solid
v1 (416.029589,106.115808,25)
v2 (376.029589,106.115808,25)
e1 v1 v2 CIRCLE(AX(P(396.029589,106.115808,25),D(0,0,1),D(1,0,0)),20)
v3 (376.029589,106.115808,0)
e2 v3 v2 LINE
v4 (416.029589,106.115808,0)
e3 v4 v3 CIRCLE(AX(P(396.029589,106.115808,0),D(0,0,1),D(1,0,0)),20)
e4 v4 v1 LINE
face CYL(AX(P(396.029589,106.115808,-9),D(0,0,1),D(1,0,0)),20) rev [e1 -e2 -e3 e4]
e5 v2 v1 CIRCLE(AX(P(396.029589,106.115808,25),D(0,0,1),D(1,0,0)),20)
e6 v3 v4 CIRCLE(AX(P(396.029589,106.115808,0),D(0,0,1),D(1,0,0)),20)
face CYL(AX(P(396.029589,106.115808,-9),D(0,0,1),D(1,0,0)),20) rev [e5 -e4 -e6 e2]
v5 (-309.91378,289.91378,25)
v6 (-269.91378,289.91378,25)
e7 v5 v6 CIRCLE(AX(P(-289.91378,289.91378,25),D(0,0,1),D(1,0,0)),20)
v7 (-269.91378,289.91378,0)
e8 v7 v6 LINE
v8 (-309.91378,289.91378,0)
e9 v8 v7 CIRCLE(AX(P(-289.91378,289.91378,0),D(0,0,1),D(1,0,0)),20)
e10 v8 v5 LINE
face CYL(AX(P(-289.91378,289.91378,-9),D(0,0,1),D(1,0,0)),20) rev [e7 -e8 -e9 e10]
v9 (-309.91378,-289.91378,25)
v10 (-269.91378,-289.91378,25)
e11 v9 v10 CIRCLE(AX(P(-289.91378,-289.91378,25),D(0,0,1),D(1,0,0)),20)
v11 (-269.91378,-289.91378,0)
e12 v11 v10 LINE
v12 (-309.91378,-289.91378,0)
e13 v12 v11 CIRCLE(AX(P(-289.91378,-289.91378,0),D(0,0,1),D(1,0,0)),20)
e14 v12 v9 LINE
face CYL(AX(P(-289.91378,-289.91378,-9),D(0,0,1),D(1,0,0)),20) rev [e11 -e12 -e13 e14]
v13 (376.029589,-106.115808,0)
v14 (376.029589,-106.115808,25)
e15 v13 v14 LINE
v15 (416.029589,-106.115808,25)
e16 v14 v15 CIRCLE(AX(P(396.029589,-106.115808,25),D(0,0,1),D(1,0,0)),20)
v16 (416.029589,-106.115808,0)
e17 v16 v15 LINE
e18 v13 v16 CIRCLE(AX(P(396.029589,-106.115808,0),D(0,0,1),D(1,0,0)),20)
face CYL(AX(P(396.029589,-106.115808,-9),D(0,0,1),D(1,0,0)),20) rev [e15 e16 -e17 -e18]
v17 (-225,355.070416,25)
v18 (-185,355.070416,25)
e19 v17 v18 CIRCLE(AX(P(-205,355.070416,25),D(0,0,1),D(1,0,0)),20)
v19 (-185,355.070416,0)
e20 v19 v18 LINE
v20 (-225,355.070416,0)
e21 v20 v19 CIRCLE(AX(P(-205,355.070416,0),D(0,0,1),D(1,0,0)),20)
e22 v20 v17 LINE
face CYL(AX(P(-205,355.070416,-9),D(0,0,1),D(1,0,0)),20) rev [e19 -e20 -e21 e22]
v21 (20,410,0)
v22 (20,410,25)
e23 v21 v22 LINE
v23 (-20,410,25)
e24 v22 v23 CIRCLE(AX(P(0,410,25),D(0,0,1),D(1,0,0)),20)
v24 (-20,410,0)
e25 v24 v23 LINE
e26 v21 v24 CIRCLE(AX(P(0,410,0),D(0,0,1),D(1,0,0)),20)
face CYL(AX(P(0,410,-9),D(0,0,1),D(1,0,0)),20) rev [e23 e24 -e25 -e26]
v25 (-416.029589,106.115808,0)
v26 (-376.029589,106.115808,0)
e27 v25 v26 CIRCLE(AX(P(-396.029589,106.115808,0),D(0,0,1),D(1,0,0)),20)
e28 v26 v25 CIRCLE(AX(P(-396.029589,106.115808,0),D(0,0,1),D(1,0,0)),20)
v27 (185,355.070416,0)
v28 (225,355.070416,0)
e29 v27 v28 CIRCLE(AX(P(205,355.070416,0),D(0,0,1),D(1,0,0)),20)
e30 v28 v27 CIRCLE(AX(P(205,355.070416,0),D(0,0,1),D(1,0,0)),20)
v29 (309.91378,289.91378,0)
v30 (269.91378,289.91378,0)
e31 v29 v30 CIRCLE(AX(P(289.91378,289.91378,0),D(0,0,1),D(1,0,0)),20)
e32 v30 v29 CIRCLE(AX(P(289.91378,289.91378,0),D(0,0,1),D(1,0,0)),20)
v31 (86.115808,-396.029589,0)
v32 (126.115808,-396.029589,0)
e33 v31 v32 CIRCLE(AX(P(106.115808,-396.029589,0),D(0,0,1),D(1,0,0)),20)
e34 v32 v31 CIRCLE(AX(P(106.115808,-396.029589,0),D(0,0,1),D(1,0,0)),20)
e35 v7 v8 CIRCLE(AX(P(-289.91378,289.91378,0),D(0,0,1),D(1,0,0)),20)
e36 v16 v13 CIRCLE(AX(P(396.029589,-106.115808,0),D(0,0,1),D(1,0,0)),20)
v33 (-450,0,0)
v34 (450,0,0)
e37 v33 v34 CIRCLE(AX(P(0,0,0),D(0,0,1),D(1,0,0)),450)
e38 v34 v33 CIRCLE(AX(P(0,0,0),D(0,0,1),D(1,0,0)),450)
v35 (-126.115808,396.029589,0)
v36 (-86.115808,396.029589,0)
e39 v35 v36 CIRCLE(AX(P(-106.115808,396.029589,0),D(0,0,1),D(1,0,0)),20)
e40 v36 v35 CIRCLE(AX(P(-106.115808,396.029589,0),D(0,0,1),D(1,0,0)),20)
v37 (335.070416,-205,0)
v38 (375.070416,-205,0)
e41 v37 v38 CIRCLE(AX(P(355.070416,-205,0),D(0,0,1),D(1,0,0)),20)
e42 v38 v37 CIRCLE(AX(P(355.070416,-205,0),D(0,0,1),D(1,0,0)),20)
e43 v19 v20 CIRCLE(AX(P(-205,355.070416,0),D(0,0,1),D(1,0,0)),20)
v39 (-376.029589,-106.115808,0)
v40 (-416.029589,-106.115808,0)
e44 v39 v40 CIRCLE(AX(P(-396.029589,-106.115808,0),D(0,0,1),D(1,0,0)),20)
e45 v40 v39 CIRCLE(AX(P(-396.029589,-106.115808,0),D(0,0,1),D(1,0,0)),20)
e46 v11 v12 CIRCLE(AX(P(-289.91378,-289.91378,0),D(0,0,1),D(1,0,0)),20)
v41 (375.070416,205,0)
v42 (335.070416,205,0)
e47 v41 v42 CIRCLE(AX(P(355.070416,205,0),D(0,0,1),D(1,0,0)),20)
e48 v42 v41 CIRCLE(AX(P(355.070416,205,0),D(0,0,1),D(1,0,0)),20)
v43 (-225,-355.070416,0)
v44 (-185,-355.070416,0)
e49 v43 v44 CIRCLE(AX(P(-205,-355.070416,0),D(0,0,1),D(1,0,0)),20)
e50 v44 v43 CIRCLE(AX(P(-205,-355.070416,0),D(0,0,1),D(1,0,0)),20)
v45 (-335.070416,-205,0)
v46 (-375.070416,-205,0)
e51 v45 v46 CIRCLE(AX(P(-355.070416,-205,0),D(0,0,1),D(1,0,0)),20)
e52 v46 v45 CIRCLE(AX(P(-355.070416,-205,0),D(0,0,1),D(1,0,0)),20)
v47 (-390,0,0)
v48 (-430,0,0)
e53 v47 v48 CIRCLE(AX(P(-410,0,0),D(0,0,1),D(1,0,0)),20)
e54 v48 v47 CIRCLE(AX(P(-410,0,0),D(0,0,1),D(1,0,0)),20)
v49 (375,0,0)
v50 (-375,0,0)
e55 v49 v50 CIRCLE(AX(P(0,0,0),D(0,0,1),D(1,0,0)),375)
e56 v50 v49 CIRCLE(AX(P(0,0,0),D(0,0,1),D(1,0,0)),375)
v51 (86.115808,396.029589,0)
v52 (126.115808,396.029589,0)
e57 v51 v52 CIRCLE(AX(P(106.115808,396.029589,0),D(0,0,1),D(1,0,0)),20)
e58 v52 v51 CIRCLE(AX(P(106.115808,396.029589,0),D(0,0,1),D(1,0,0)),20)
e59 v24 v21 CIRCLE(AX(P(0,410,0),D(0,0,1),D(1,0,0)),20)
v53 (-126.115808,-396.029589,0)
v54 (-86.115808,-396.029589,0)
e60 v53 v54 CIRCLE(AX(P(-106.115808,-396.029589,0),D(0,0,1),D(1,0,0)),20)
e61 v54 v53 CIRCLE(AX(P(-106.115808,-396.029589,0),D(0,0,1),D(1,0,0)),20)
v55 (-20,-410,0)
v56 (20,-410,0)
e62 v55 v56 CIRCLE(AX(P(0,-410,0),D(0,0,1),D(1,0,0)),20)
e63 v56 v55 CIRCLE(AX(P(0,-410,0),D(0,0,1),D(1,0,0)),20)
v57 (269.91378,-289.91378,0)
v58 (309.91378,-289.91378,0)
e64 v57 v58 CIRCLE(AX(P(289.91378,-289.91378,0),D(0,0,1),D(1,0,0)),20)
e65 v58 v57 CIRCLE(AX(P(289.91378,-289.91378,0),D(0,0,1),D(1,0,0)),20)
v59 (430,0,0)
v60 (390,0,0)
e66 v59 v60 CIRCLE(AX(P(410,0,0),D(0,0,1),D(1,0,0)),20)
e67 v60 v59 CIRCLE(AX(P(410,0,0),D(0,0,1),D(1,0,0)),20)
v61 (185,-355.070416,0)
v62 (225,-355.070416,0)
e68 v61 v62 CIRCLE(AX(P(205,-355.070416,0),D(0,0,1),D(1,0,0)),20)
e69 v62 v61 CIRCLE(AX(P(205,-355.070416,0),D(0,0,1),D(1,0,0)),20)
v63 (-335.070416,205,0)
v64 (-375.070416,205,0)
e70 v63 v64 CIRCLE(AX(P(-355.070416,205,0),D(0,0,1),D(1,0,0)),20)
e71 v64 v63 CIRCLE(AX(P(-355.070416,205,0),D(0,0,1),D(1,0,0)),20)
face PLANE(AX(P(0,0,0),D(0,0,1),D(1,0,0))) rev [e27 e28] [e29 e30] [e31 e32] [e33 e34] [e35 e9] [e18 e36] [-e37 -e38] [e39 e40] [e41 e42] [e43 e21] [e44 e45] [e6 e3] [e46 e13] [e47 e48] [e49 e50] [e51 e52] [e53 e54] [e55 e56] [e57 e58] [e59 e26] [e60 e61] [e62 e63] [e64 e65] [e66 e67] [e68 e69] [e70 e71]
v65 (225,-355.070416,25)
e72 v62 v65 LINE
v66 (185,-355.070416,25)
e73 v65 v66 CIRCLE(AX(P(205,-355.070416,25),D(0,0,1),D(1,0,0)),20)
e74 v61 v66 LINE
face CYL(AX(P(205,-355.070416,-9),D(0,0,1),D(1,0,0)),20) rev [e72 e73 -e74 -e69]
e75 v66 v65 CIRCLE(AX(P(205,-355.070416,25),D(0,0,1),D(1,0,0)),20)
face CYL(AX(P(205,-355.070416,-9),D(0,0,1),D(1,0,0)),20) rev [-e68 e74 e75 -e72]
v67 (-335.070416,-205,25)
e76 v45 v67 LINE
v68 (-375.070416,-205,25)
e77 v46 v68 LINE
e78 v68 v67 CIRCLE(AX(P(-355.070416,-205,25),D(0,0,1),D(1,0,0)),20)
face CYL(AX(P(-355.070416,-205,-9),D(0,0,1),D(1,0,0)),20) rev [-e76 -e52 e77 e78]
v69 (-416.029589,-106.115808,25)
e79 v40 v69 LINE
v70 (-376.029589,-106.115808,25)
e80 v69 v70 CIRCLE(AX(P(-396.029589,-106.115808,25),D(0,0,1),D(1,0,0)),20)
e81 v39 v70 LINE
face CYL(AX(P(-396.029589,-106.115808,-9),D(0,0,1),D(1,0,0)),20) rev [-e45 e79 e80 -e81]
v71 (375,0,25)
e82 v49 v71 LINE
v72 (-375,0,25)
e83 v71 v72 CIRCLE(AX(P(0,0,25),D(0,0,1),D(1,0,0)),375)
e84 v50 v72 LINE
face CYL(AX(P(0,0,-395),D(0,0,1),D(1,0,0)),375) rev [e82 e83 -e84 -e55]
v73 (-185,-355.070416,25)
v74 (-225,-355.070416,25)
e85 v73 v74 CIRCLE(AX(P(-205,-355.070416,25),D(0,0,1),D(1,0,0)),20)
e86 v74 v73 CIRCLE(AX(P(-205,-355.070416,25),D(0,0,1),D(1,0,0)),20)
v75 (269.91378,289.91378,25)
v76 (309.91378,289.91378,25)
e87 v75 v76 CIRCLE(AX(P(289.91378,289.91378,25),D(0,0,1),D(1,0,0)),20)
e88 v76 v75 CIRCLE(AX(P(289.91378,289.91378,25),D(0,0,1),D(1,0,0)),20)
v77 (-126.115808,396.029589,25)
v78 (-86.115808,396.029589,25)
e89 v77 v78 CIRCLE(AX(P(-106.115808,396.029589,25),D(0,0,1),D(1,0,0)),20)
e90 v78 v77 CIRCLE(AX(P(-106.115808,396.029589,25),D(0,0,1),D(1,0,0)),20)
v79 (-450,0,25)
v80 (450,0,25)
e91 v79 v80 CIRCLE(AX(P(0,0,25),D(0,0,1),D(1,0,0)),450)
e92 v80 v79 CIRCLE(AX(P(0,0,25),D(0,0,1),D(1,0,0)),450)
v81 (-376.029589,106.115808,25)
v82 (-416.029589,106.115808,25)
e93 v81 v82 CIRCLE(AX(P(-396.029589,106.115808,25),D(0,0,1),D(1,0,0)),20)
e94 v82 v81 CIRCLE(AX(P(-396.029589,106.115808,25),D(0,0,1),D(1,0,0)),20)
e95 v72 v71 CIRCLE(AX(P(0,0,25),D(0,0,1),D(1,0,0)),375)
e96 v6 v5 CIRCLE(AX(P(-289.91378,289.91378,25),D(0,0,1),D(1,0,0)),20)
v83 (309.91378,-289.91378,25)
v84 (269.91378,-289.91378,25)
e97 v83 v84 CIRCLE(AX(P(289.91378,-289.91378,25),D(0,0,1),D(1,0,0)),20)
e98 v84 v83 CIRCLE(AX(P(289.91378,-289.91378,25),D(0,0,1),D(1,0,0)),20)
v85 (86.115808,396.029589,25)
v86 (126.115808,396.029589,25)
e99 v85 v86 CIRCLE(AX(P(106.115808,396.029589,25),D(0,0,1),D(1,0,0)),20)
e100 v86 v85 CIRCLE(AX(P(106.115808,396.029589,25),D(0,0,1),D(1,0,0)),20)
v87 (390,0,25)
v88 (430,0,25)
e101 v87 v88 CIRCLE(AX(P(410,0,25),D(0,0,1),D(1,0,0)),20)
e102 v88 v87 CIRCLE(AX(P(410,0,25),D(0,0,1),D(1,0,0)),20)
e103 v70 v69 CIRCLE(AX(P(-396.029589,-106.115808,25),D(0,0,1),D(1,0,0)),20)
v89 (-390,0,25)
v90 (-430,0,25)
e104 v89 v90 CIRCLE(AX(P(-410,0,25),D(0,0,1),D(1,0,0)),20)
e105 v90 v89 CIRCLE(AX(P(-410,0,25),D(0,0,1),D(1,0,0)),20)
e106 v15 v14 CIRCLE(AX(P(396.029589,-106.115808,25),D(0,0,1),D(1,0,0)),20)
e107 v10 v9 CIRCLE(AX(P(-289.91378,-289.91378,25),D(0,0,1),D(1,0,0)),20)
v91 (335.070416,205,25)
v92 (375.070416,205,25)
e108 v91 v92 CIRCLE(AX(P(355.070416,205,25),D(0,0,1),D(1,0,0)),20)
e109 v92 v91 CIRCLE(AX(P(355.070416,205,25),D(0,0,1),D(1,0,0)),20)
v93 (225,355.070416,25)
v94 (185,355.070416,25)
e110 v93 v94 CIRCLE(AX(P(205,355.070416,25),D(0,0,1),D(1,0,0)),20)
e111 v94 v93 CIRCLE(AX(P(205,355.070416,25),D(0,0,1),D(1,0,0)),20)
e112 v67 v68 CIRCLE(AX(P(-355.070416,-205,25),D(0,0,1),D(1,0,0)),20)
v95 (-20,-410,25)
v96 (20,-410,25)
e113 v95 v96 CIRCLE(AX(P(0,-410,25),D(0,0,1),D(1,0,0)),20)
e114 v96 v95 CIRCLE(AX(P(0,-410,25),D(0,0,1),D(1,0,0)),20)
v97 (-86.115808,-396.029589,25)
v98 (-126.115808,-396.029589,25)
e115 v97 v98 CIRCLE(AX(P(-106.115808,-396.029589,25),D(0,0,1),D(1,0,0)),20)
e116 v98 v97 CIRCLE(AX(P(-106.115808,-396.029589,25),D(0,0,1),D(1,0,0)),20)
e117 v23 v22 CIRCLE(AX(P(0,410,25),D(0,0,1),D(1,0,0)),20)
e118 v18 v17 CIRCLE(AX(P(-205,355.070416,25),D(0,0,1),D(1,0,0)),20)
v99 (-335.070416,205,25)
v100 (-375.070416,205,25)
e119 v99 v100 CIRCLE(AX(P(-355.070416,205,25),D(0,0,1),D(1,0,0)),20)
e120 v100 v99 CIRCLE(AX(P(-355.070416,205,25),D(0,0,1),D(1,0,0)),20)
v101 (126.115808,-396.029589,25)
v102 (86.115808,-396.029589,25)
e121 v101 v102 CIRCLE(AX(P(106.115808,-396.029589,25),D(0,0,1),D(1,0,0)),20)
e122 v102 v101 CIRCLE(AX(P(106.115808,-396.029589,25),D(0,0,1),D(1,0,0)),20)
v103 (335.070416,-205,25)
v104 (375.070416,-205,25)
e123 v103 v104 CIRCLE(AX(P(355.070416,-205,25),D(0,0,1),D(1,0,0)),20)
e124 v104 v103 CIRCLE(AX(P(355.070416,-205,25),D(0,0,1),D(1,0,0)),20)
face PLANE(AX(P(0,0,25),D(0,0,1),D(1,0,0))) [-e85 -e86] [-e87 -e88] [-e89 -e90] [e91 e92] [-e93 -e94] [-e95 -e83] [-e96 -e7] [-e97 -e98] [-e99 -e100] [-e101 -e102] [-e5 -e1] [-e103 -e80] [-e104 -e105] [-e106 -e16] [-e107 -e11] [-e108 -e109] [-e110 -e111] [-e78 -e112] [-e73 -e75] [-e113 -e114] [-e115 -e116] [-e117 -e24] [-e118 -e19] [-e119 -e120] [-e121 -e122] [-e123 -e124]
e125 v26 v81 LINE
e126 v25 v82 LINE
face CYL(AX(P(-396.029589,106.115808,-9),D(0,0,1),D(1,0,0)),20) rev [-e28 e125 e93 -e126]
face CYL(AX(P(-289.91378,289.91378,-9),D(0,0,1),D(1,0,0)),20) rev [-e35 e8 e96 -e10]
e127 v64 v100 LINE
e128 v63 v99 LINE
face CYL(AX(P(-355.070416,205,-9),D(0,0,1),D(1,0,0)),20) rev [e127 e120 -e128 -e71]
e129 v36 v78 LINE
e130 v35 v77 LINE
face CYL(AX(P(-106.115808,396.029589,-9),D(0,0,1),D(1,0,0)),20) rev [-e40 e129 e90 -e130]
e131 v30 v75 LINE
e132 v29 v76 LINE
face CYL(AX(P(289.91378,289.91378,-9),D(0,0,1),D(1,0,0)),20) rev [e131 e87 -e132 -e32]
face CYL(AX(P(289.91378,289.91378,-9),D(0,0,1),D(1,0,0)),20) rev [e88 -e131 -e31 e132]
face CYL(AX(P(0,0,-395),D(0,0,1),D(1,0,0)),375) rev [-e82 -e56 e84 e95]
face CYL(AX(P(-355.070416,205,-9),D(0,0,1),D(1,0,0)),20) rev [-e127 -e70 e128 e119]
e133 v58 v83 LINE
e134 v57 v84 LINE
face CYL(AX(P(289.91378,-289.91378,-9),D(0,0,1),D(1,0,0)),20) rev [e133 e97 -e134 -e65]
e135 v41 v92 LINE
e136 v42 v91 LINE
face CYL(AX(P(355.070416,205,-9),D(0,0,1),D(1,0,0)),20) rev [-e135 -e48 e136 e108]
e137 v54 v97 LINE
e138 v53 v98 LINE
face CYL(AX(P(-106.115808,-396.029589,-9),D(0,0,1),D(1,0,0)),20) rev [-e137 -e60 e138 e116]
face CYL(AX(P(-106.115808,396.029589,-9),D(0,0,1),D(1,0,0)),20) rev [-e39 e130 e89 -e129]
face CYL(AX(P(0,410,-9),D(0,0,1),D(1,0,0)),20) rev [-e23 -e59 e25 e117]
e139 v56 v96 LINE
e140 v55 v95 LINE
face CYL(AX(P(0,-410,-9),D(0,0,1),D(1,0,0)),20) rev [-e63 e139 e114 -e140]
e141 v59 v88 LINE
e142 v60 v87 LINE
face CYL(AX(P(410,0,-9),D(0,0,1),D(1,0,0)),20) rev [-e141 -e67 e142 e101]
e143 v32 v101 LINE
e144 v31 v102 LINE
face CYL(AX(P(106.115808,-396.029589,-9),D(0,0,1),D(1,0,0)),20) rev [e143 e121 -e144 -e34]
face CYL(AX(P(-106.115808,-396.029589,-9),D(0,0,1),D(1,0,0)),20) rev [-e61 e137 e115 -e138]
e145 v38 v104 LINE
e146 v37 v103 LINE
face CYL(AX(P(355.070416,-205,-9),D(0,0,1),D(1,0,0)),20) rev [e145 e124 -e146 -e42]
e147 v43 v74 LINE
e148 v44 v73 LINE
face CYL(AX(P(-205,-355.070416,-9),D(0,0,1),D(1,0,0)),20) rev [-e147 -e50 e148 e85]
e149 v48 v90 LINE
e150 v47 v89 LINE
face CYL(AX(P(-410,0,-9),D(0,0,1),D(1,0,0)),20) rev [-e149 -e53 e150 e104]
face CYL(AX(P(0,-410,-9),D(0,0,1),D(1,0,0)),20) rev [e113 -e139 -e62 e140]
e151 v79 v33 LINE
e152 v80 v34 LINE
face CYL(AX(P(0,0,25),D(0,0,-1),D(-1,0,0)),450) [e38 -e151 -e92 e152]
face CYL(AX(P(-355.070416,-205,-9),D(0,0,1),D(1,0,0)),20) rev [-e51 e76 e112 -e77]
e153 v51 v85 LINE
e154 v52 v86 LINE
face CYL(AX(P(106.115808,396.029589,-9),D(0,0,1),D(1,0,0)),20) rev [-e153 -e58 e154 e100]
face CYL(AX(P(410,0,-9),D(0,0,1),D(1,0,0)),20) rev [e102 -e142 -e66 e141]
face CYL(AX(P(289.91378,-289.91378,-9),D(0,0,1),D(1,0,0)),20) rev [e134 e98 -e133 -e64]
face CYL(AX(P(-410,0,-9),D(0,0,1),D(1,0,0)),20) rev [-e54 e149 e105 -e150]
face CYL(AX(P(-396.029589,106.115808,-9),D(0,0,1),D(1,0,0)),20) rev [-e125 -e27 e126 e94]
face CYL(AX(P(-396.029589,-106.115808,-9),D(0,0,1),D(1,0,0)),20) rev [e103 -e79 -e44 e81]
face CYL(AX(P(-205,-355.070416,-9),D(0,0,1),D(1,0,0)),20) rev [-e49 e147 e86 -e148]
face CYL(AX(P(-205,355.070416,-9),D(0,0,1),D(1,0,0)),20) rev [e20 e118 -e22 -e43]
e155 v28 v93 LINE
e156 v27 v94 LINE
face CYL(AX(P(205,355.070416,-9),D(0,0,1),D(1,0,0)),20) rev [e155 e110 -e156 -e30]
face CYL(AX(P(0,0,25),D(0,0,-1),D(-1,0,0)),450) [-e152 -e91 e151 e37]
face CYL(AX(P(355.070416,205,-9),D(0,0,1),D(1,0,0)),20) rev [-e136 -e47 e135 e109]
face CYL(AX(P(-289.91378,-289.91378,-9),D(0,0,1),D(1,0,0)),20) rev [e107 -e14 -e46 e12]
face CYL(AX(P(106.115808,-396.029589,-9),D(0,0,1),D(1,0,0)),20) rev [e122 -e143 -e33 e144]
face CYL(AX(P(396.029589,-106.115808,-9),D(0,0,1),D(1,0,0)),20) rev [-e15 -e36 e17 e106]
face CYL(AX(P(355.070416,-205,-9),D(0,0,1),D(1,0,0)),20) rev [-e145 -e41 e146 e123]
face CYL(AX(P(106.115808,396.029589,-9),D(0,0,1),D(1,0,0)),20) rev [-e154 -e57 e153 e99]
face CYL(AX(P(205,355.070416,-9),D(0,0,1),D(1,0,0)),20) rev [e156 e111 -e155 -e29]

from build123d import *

# Parameters (mm, degrees)
SKETCH_1_R          = 450
EXTRUDE_1_DEPTH     = 25
SKETCH_2_R          = 20
CUT_EXTRUDE_1_DEPTH = 34
SKETCH_3_R          = 375
CUT_EXTRUDE_2_DEPTH = 420


with BuildPart() as part:
    # 草图1 → 凸台-拉伸1 (new body)
    with BuildSketch(Plane.XY):
        Circle(SKETCH_1_R)
    extrude(amount=EXTRUDE_1_DEPTH)

    # 草图2 → 切除-拉伸1 (cut)
    with BuildSketch(Plane.XY.offset(25)):
        with Locations((0, 410)):
            Circle(SKETCH_2_R)
        with Locations((106.115808492, 396.029588779)):
            Circle(SKETCH_2_R)
        with Locations((205, 355.070415552)):
            Circle(SKETCH_2_R)
        with Locations((289.913780286, 289.913780286)):
            Circle(SKETCH_2_R)
        with Locations((355.070415552, 205)):
            Circle(SKETCH_2_R)
        with Locations((396.029588779, 106.115808492)):
            Circle(SKETCH_2_R)
        with Locations((410, 0)):
            Circle(SKETCH_2_R)
        with Locations((396.029588779, -106.115808492)):
            Circle(SKETCH_2_R)
        with Locations((355.070415552, -205)):
            Circle(SKETCH_2_R)
        with Locations((289.913780286, -289.913780286)):
            Circle(SKETCH_2_R)
        with Locations((205, -355.070415552)):
            Circle(SKETCH_2_R)
        with Locations((106.115808492, -396.029588779)):
            Circle(SKETCH_2_R)
        with Locations((0, -410)):
            Circle(SKETCH_2_R)
        with Locations((-106.115808492, -396.029588779)):
            Circle(SKETCH_2_R)
        with Locations((-205, -355.070415552)):
            Circle(SKETCH_2_R)
        with Locations((-289.913780286, -289.913780286)):
            Circle(SKETCH_2_R)
        with Locations((-355.070415552, -205)):
            Circle(SKETCH_2_R)
        with Locations((-396.029588779, -106.115808492)):
            Circle(SKETCH_2_R)
        with Locations((-410, 0)):
            Circle(SKETCH_2_R)
        with Locations((-396.029588779, 106.115808492)):
            Circle(SKETCH_2_R)
        with Locations((-355.070415552, 205)):
            Circle(SKETCH_2_R)
        with Locations((-289.913780286, 289.913780286)):
            Circle(SKETCH_2_R)
        with Locations((-205, 355.070415552)):
            Circle(SKETCH_2_R)
        with Locations((-106.115808492, 396.029588779)):
            Circle(SKETCH_2_R)
    extrude(amount=-CUT_EXTRUDE_1_DEPTH, mode=Mode.SUBTRACT)

    # 草图3 → 切除-拉伸2 (cut)
    with BuildSketch(Plane.XY.offset(25)):
        Circle(SKETCH_3_R)
    extrude(amount=-CUT_EXTRUDE_2_DEPTH, mode=Mode.SUBTRACT)


solid = part.part
